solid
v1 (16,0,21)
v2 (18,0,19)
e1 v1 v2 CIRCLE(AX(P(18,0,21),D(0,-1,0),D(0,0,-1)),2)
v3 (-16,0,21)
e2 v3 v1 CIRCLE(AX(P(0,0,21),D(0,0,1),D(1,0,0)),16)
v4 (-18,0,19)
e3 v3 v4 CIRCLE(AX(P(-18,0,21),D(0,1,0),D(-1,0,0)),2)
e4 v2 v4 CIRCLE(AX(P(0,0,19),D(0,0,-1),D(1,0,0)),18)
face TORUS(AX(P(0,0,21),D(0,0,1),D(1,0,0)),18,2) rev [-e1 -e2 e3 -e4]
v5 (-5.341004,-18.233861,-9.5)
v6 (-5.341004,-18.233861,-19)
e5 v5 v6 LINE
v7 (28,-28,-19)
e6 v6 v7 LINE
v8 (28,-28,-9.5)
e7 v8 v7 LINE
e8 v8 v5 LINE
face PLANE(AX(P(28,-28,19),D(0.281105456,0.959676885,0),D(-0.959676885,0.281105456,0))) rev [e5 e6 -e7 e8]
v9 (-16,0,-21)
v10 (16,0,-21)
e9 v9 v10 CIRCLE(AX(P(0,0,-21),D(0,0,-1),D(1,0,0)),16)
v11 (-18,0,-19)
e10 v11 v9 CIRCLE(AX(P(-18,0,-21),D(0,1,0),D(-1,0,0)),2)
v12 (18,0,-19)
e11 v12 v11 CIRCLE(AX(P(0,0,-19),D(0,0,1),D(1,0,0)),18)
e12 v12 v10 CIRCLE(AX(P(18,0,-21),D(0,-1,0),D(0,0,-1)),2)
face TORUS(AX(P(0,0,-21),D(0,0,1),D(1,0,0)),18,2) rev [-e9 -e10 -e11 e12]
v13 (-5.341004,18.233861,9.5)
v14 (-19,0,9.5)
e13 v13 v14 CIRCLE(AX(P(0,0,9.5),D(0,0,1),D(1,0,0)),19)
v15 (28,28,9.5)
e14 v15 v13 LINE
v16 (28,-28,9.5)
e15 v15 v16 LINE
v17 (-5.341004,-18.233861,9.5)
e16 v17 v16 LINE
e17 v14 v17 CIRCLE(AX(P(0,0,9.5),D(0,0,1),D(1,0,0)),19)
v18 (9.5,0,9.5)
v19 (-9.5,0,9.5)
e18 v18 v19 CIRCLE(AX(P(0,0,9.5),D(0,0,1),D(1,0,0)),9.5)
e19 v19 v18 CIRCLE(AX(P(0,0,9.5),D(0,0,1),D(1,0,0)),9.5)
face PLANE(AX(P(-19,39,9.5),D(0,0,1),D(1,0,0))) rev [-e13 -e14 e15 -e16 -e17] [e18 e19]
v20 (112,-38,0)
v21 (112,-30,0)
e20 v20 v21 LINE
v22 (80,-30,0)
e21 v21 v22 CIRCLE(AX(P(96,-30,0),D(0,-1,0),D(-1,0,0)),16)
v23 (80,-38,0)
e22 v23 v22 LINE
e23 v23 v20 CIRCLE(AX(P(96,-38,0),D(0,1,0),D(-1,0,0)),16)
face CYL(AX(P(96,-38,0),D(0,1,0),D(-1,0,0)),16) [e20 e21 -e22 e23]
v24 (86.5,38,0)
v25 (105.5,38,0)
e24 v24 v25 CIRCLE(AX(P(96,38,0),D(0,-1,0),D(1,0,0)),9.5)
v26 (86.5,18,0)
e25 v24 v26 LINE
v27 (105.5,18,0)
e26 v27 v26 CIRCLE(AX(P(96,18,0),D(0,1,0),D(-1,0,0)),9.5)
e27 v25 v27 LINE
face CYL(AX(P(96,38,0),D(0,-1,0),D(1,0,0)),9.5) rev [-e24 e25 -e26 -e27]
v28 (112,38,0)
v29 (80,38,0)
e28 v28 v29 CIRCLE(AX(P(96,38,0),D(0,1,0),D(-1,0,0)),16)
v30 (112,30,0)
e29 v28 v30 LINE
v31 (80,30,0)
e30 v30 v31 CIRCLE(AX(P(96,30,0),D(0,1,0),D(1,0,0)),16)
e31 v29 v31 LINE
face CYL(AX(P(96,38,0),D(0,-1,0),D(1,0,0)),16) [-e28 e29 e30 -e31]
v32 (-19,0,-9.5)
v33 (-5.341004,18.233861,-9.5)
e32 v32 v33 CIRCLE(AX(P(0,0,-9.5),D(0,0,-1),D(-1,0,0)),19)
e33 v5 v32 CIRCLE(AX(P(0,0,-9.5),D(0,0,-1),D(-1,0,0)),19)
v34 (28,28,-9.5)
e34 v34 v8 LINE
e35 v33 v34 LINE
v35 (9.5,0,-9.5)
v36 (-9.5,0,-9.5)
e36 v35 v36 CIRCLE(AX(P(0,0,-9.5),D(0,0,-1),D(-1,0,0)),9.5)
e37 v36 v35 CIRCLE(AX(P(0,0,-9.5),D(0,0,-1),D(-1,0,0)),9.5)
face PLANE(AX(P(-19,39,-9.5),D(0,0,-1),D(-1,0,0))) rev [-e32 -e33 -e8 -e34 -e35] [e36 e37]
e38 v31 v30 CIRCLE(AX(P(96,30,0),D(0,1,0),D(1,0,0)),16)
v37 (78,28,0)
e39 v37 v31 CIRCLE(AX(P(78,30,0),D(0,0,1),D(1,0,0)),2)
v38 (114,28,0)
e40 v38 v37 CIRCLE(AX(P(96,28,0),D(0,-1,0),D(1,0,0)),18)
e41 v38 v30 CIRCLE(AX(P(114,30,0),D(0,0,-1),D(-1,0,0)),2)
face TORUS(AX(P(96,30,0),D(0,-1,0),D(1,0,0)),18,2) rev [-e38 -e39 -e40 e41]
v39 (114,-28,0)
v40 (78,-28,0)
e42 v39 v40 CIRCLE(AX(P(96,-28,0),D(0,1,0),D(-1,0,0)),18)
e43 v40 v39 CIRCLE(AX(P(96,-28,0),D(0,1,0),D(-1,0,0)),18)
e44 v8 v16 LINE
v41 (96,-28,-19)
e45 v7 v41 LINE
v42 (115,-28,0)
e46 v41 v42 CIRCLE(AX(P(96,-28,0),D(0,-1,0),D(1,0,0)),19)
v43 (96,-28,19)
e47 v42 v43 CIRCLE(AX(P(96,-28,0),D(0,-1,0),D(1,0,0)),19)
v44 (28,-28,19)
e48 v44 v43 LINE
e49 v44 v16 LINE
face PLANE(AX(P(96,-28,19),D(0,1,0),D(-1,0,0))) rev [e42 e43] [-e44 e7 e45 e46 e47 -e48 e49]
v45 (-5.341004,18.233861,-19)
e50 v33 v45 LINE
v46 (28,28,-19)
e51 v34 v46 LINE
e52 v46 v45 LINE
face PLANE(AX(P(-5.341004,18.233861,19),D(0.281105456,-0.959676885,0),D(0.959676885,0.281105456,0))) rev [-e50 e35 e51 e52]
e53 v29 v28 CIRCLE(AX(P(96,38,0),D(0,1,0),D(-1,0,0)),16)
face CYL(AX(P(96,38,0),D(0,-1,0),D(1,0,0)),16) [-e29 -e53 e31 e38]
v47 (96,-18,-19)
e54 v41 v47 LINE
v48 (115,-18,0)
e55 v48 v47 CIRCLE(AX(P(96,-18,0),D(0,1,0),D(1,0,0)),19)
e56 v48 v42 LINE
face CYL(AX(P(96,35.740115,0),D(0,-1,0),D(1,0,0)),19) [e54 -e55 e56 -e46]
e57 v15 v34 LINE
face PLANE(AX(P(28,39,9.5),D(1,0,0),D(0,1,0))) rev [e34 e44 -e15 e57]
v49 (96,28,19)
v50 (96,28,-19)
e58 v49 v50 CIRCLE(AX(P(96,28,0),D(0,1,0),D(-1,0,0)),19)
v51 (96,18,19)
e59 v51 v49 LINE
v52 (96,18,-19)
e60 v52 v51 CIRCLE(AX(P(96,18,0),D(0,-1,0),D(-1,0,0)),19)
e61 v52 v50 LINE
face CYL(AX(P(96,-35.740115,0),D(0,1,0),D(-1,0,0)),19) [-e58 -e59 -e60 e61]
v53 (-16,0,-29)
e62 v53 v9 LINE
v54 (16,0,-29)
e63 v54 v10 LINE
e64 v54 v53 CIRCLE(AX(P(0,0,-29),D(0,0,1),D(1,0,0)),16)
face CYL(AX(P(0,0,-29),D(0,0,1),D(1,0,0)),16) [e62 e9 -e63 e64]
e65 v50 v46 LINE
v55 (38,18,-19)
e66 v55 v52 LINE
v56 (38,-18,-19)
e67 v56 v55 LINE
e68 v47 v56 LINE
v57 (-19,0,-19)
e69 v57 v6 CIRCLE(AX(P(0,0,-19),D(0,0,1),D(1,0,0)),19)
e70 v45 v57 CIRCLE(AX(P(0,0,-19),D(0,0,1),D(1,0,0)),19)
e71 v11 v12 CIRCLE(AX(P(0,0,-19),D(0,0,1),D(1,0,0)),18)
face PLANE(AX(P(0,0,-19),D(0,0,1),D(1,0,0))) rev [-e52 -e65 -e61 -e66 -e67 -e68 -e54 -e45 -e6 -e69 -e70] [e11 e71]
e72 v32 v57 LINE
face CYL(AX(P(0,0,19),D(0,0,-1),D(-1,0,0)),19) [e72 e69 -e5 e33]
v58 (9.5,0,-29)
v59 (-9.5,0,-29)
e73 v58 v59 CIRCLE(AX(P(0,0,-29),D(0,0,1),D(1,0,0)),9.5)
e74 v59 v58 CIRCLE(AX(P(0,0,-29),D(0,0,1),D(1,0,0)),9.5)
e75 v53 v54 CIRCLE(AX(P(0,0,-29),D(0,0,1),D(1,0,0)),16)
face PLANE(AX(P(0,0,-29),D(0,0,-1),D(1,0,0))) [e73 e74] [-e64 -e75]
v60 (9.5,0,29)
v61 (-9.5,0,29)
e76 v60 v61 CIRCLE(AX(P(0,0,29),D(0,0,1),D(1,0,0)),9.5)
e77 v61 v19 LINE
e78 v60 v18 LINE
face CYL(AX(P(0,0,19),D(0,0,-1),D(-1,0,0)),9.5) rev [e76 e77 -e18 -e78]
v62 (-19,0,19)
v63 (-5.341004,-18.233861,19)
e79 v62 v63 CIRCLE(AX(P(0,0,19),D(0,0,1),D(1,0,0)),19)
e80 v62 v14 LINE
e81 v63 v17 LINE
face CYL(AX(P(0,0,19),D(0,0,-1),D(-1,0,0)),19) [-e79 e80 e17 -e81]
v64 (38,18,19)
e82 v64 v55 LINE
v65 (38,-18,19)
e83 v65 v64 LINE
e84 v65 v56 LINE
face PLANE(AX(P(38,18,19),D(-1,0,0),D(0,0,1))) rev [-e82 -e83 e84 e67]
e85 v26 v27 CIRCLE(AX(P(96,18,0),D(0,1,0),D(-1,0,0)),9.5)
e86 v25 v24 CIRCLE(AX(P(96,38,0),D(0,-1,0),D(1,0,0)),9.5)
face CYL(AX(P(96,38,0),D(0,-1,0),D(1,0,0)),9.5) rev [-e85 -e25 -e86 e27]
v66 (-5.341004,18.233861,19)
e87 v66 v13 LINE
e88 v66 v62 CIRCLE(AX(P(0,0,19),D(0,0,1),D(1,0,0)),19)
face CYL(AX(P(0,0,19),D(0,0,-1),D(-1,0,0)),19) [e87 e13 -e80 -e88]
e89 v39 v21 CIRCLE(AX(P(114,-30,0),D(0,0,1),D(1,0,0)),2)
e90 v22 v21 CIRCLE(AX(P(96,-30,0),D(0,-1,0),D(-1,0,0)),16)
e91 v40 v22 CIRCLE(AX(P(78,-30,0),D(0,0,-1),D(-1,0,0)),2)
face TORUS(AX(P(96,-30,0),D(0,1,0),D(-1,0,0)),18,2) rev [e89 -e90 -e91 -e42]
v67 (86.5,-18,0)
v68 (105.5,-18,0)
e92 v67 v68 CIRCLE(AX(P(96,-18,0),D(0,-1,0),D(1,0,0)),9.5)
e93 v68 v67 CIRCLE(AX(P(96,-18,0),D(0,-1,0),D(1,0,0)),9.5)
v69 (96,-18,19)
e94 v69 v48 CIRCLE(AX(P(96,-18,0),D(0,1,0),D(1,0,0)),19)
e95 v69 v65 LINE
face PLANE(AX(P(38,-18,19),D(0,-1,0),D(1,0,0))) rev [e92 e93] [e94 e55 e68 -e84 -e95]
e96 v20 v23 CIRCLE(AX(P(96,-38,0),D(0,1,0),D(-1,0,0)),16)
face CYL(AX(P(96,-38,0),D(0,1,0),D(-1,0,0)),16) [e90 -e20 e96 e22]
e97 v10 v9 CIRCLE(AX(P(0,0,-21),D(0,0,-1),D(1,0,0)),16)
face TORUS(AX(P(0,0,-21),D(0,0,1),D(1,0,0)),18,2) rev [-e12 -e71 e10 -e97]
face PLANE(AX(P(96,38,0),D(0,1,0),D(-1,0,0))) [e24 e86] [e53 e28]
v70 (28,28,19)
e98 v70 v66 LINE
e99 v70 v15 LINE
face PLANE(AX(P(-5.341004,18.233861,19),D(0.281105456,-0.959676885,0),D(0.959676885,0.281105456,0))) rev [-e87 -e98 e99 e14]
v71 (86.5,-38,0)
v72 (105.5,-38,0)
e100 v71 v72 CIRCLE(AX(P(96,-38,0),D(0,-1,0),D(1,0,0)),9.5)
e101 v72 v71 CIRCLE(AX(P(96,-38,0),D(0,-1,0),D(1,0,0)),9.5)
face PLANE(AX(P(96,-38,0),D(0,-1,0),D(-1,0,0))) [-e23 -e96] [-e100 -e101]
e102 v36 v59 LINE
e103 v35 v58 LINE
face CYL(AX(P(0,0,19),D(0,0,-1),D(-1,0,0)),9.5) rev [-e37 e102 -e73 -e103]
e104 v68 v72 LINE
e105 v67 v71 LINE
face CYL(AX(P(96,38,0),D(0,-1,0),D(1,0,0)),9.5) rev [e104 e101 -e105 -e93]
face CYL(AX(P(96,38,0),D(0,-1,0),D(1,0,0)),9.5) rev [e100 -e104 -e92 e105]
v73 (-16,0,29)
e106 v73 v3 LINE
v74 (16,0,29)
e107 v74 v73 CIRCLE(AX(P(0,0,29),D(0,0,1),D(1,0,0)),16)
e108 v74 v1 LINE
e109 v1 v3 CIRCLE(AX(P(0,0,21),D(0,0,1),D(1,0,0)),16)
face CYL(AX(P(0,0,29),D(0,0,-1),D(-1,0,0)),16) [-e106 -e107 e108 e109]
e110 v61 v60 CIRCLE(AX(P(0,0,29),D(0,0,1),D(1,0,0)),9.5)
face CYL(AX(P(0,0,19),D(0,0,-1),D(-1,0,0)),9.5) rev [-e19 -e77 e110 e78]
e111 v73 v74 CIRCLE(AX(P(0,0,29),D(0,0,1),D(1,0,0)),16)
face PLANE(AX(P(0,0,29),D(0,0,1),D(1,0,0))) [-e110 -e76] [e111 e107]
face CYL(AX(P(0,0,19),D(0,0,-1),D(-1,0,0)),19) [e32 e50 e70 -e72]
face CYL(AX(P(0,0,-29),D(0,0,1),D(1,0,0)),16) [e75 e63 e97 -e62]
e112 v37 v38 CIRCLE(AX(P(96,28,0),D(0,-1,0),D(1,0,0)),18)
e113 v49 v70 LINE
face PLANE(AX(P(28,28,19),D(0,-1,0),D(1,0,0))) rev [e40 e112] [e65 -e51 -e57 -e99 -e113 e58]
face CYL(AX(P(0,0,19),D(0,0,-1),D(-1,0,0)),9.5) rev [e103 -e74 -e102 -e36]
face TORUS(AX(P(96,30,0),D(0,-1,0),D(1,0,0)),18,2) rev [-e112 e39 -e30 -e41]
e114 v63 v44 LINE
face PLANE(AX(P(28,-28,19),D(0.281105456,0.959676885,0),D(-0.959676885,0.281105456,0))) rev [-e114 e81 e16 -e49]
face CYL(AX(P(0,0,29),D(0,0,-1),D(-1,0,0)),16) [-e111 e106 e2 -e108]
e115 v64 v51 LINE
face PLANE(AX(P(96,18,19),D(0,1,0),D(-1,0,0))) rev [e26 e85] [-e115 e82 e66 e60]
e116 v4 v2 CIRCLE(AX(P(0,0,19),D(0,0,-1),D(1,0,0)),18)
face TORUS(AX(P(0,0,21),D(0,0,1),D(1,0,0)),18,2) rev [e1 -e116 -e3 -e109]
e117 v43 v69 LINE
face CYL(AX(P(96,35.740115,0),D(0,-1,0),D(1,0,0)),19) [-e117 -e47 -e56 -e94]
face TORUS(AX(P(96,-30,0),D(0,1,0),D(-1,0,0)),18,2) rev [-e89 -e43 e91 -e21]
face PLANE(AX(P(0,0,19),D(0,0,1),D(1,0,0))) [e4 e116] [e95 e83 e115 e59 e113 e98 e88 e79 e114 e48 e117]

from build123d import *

# Parameters (mm, degrees)
LINK_BODY_PROFILE_SKETCH_R = 9.5
LINK_BODY_38MM_DEPTH       = 19
FORK_END_BOSS_A_SKETCH_R   = 19
FORK_END_BOSS_A_DEPTH      = 10
FORK_START                 = -10
FORK_END_BOSS_B_SKETCH_R   = 19
FORK_END_BOSS_B_DEPTH      = 10
FORK_SLOT_SKETCH_W         = 47
FORK_SLOT_SKETCH_H         = 19
FORK_SLOT_19MM_DEPTH       = 67
SIDE_HUB_SKETCH_32_R       = 16
SIDE_HUB_SKETCH_32_R_2     = 9.5
SIDE_HUB_32_DEPTH          = 10
FORK_HUB_SKETCH_32_R       = 16
FORK_HUB_32_DEPTH          = 10
FORK_PIN_BORE_SKETCH_19_R  = 9.5
FORK_PIN_BORE_19_DEPTH     = 141.861634237
EDGE_FILLETS_R2_R          = 2


with BuildPart() as part:
    # Link Body Profile Sketch → Link Body 38mm (new, symmetric)
    with BuildSketch(Plane.XY):
        with BuildLine():
            Line((-5.341003663, 18.233860806), (28, 28))
            Line((28, 28), (96, 28))
            Line((96, 28), (96, 18))
            Line((96, 18), (38, 18))
            Line((38, 18), (38, -18))
            Line((38, -18), (96, -18))
            Line((96, -18), (96, -28))
            Line((96, -28), (28, -28))
            Line((28, -28), (-5.341003663, -18.233860806))
            ThreePointArc((-5.341003663, -18.233860806), (-19, 0), (-5.341003663, 18.233860806))
        make_face()
        Circle(LINK_BODY_PROFILE_SKETCH_R, mode=Mode.SUBTRACT)
    extrude(amount=LINK_BODY_38MM_DEPTH, both=True)

    # Fork End Boss A Sketch → Fork End Boss A (add)
    with BuildSketch(Plane(origin=(0, 28, 0), x_dir=(1, 0, 0), z_dir=(0, 1, 0))):
        with Locations((96, 0)):
            Circle(FORK_END_BOSS_A_SKETCH_R)
    extrude(amount=-FORK_END_BOSS_A_DEPTH)

    # Fork End Boss B Sketch → Fork End Boss B (add)
    with BuildSketch(Plane.XZ.offset(28).offset(FORK_START)):
        with Locations((96, 0)):
            Circle(FORK_END_BOSS_B_SKETCH_R)
    extrude(amount=FORK_END_BOSS_B_DEPTH)

    # Fork Slot Sketch → Fork Slot 19mm (cut)
    with BuildSketch(Plane.XZ.offset(28)):
        with Locations((4.5, 0)):
            Rectangle(FORK_SLOT_SKETCH_W, FORK_SLOT_SKETCH_H)
    extrude(amount=-FORK_SLOT_19MM_DEPTH, mode=Mode.SUBTRACT)

    # Side Hub Sketch Ø32 → Side Hub Ø32 (add)
    with BuildSketch(Plane.XY.offset(19)):
        Circle(SIDE_HUB_SKETCH_32_R)
        Circle(SIDE_HUB_SKETCH_32_R_2, mode=Mode.SUBTRACT)
    side_hub_32 = extrude(amount=SIDE_HUB_32_DEPTH)

    # Side Hub Mirror: Side Hub Ø32 across plane
    add(side_hub_32.mirror(Plane.XY))

    # Fork Hub Sketch Ø32 → Fork Hub Ø32 (add)
    with BuildSketch(Plane(origin=(0, 28, 0), x_dir=(1, 0, 0), z_dir=(0, 1, 0))):
        with Locations((96, 0)):
            Circle(FORK_HUB_SKETCH_32_R)
    fork_hub_32 = extrude(amount=FORK_HUB_32_DEPTH)

    # Fork Hub Mirror: Fork Hub Ø32 across plane
    add(fork_hub_32.mirror(Plane.ZX))

    # Fork Pin Bore Sketch Ø19 → Fork Pin Bore Ø19 (cut, through all)
    with BuildSketch(Plane.XZ.offset(38)):
        with Locations((96, 0)):
            Circle(FORK_PIN_BORE_SKETCH_19_R)
    extrude(amount=-FORK_PIN_BORE_19_DEPTH, mode=Mode.SUBTRACT)

    # Edge Fillets R2
    edge_fillets_r2_edges = [part.edges().sort_by_distance(p)[0] for p in [
        (80, -28, 0),
        (-16, 0, 19),
        (-16, 0, -19),
        (80, 28, 0),
    ]]
    fillet(edge_fillets_r2_edges, radius=EDGE_FILLETS_R2_R)


solid = part.part
